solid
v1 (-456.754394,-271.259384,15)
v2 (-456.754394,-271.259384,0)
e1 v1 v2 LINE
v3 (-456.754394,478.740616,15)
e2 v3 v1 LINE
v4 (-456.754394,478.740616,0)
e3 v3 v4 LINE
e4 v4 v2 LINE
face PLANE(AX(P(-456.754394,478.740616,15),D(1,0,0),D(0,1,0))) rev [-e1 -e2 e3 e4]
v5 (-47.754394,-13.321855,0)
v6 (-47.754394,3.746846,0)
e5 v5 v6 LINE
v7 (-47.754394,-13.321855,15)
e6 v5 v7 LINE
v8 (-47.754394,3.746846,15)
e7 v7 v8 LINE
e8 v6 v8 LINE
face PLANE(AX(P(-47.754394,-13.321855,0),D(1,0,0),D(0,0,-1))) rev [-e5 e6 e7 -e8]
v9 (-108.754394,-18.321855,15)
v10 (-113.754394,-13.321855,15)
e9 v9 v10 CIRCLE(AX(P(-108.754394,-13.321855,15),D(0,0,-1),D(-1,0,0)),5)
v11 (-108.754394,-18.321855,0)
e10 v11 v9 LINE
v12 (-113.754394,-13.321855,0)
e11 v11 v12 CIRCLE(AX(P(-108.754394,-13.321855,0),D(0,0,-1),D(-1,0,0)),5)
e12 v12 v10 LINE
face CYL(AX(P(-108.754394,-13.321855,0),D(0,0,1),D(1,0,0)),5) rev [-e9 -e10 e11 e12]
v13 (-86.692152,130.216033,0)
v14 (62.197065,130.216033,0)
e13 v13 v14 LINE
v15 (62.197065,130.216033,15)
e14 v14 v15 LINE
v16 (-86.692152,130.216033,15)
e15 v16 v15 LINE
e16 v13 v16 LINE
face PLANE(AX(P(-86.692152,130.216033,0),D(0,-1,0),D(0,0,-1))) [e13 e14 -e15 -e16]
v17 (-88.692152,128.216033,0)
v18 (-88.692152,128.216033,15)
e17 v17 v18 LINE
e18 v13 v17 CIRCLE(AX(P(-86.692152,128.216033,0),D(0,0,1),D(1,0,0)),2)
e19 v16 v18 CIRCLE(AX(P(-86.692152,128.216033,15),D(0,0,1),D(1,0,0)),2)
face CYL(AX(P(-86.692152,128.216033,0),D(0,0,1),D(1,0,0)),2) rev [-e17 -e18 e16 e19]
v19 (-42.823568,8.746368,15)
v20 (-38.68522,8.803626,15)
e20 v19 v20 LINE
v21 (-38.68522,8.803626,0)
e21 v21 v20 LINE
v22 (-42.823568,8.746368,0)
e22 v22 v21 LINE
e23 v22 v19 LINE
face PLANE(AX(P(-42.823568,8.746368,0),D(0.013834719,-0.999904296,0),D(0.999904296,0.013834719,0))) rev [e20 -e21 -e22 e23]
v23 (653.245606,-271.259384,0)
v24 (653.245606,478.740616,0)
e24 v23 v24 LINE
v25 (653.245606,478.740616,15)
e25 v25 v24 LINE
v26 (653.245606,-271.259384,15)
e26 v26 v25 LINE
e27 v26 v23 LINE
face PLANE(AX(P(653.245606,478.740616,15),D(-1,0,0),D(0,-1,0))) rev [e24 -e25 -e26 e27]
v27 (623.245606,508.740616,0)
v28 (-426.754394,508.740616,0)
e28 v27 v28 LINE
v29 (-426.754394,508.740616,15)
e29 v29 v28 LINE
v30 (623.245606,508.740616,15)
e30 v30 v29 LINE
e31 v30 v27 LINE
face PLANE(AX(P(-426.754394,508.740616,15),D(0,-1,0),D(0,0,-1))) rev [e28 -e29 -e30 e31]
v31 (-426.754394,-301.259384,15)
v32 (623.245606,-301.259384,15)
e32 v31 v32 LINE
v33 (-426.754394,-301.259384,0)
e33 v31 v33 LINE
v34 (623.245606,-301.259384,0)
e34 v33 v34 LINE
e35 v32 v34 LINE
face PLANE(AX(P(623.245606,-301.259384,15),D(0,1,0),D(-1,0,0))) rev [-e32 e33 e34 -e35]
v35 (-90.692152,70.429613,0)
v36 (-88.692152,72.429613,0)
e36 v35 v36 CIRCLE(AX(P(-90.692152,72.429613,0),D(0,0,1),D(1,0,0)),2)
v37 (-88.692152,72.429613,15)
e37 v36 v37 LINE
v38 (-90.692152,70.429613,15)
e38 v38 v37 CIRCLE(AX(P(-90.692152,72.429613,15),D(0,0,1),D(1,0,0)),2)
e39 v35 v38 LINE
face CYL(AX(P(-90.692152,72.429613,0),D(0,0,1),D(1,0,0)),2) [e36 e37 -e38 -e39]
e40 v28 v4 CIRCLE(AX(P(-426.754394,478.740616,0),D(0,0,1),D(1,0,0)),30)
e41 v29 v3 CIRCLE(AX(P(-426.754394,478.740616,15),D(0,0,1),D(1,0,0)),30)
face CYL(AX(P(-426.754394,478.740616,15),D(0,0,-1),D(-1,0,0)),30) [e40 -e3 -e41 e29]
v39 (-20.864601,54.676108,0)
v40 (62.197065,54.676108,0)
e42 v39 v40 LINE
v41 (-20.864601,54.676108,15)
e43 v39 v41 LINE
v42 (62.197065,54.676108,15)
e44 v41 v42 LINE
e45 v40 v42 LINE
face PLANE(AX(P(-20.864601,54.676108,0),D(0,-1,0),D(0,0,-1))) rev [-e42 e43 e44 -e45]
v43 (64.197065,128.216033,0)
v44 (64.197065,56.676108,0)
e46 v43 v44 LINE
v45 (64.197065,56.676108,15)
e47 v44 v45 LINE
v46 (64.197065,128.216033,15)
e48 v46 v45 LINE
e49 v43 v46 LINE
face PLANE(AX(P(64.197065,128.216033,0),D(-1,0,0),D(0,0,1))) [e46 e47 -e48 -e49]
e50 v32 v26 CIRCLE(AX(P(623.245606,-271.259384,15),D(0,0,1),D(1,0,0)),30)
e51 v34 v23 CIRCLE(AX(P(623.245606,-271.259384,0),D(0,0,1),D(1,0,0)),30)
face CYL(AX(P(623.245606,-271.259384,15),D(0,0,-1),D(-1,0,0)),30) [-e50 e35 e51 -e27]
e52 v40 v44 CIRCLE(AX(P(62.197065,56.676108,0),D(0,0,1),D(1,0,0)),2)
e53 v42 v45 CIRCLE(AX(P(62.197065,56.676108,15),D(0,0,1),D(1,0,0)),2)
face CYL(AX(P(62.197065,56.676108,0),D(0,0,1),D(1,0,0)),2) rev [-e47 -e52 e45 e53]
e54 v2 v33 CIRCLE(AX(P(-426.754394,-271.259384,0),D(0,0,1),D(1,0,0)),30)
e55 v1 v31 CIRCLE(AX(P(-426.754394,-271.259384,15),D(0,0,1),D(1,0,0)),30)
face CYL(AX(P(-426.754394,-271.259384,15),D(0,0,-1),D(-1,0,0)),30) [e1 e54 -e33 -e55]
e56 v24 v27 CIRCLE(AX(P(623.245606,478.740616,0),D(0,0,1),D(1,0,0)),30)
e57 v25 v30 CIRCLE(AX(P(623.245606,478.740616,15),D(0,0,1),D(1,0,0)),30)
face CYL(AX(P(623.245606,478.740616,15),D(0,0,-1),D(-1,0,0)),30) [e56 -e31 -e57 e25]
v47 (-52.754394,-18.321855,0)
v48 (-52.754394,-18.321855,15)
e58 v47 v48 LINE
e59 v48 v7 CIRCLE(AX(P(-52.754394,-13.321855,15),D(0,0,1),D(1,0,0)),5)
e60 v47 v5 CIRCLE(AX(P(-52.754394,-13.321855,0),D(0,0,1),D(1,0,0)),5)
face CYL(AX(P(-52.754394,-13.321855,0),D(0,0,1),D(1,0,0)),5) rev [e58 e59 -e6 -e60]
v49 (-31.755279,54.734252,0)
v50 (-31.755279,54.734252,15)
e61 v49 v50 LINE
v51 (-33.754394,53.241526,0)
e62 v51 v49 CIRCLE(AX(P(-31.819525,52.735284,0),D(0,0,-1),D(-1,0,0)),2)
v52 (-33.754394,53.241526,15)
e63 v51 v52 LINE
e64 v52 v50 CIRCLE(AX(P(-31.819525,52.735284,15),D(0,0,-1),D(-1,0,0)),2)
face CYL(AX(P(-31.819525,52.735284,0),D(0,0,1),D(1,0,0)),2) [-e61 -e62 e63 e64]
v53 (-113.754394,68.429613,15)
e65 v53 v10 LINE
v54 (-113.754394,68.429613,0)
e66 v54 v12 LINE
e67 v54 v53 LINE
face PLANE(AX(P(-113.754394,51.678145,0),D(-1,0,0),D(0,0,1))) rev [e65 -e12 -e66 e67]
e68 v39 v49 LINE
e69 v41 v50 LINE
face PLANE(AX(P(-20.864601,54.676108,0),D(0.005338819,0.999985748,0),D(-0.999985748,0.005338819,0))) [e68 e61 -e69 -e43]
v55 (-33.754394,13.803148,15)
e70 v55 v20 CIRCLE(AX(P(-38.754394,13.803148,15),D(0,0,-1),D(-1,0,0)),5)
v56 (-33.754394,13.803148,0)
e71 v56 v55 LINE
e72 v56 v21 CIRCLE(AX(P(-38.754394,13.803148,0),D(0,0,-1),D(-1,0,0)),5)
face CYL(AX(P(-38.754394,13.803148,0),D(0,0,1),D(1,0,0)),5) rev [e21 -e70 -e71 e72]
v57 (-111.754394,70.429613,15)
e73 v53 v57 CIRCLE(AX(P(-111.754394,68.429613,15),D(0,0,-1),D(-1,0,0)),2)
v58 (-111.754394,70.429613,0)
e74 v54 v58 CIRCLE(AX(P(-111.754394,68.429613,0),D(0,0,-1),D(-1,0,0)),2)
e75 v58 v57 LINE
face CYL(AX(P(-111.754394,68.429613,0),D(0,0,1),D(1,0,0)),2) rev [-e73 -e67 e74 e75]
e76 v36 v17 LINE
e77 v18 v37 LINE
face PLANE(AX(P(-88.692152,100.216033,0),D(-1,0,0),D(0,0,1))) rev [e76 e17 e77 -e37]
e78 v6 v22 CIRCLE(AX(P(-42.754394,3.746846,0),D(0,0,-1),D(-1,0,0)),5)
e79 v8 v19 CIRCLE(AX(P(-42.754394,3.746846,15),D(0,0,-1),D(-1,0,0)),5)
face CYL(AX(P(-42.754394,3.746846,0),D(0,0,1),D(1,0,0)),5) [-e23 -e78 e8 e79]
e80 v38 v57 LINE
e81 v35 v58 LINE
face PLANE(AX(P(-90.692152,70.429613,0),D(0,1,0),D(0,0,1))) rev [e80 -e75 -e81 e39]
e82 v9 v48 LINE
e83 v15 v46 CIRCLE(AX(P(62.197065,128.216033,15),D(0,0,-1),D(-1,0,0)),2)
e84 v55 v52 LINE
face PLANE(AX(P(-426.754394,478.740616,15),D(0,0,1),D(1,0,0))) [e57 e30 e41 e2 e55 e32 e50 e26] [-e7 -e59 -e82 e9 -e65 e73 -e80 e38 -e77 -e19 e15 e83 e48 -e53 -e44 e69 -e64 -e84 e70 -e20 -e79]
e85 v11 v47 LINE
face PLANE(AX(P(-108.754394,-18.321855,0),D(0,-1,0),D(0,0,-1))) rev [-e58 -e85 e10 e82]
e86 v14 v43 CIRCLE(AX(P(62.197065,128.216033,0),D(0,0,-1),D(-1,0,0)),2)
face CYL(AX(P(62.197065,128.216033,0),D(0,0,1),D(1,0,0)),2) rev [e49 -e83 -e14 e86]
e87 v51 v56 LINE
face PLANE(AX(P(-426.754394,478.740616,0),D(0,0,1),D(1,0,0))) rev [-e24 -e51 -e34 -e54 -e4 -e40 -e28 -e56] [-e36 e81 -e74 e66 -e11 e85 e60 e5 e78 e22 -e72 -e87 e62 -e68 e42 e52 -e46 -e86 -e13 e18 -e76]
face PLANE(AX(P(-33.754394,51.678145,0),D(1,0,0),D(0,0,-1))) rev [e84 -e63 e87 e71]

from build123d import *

# Parameters (mm, degrees)
EXTRUDE_1_DEPTH     = 15
CUT_EXTRUDE_1_DEPTH = 829.113419972


with BuildPart() as part:
    # 草图1 → 凸台-拉伸1 (new body)
    with BuildSketch(Plane.XY):
        with BuildLine():
            Line((-456.754393923, 478.74061611), (-456.754393923, -271.25938389))
            ThreePointArc((-456.754393923, -271.25938389), (-447.967597359, -292.472587326), (-426.754393923, -301.25938389))
            Line((-426.754393923, -301.25938389), (623.245606077, -301.25938389))
            ThreePointArc((623.245606077, -301.25938389), (644.458809512, -292.472587326), (653.245606077, -271.25938389))
            Line((653.245606077, -271.25938389), (653.245606077, 478.74061611))
            ThreePointArc((653.245606077, 478.74061611), (644.458809512, 499.953819545), (623.245606077, 508.74061611))
            Line((623.245606077, 508.74061611), (-426.754393923, 508.74061611))
            ThreePointArc((-426.754393923, 508.74061611), (-447.967597359, 499.953819545), (-456.754393923, 478.74061611))
        make_face()
    extrude(amount=EXTRUDE_1_DEPTH)

    # 草图2 → 切除-拉伸1 (cut, through all)
    with BuildSketch(Plane.XY.offset(15)):
        with BuildLine():
            Line((-113.754393923, 51.678144789), (-113.754393923, -13.321855211))
            ThreePointArc((-113.754393923, -13.321855211), (-112.289927829, -16.857389117), (-108.754393923, -18.321855211))
            Line((-108.754393923, -18.321855211), (-52.754393923, -18.321855211))
            ThreePointArc((-52.754393923, -18.321855211), (-49.218860017, -16.857389117), (-47.754393923, -13.321855211))
            Line((-47.754393923, -13.321855211), (-47.754393923, 3.746846437))
            ThreePointArc((-47.754393923, 3.746846437), (-46.31430038, 7.257838606), (-42.823567517, 8.746367915))
            Line((-42.823567517, 8.746367915), (-38.68522033, 8.803626264))
            ThreePointArc((-38.68522033, 8.803626264), (-35.194487466, 10.292155573), (-33.754393923, 13.803147743))
            Line((-33.754393923, 13.803147743), (-33.754393923, 51.678144789))
            Line((-33.754393923, 51.678144789), (-33.754393923, 53.24152579))
            ThreePointArc((-33.754393923, 53.24152579), (-33.016130918, 54.337823849), (-31.755279488, 54.734252116))
            Line((-31.755279488, 54.734252116), (-20.864600558, 54.67610792))
            Line((-20.864600558, 54.67610792), (62.197064842, 54.67610792))
            ThreePointArc((62.197064842, 54.67610792), (63.611278404, 55.261894358), (64.197064842, 56.67610792))
            Line((64.197064842, 56.67610792), (64.197064842, 89.975586232))
            Line((64.197064842, 89.975586232), (64.197064842, 128.216032673))
            ThreePointArc((64.197064842, 128.216032673), (63.611278404, 129.630246236), (62.197064842, 130.216032673))
            Line((62.197064842, 130.216032673), (-86.692151935, 130.216032673))
            ThreePointArc((-86.692151935, 130.216032673), (-88.106365497, 129.630246236), (-88.692151935, 128.216032673))
            Line((-88.692151935, 128.216032673), (-88.692151935, 100.216032673))
            Line((-88.692151935, 100.216032673), (-88.692151935, 72.429613021))
            ThreePointArc((-88.692151935, 72.429613021), (-89.277938372, 71.015399459), (-90.692151935, 70.429613021))
            Line((-90.692151935, 70.429613021), (-111.754393923, 70.429613021))
            ThreePointArc((-111.754393923, 70.429613021), (-113.168607486, 69.843826583), (-113.754393923, 68.429613021))
            Line((-113.754393923, 68.429613021), (-113.754393923, 51.678144789))
        make_face()
    extrude(amount=-CUT_EXTRUDE_1_DEPTH, mode=Mode.SUBTRACT)


solid = part.part
